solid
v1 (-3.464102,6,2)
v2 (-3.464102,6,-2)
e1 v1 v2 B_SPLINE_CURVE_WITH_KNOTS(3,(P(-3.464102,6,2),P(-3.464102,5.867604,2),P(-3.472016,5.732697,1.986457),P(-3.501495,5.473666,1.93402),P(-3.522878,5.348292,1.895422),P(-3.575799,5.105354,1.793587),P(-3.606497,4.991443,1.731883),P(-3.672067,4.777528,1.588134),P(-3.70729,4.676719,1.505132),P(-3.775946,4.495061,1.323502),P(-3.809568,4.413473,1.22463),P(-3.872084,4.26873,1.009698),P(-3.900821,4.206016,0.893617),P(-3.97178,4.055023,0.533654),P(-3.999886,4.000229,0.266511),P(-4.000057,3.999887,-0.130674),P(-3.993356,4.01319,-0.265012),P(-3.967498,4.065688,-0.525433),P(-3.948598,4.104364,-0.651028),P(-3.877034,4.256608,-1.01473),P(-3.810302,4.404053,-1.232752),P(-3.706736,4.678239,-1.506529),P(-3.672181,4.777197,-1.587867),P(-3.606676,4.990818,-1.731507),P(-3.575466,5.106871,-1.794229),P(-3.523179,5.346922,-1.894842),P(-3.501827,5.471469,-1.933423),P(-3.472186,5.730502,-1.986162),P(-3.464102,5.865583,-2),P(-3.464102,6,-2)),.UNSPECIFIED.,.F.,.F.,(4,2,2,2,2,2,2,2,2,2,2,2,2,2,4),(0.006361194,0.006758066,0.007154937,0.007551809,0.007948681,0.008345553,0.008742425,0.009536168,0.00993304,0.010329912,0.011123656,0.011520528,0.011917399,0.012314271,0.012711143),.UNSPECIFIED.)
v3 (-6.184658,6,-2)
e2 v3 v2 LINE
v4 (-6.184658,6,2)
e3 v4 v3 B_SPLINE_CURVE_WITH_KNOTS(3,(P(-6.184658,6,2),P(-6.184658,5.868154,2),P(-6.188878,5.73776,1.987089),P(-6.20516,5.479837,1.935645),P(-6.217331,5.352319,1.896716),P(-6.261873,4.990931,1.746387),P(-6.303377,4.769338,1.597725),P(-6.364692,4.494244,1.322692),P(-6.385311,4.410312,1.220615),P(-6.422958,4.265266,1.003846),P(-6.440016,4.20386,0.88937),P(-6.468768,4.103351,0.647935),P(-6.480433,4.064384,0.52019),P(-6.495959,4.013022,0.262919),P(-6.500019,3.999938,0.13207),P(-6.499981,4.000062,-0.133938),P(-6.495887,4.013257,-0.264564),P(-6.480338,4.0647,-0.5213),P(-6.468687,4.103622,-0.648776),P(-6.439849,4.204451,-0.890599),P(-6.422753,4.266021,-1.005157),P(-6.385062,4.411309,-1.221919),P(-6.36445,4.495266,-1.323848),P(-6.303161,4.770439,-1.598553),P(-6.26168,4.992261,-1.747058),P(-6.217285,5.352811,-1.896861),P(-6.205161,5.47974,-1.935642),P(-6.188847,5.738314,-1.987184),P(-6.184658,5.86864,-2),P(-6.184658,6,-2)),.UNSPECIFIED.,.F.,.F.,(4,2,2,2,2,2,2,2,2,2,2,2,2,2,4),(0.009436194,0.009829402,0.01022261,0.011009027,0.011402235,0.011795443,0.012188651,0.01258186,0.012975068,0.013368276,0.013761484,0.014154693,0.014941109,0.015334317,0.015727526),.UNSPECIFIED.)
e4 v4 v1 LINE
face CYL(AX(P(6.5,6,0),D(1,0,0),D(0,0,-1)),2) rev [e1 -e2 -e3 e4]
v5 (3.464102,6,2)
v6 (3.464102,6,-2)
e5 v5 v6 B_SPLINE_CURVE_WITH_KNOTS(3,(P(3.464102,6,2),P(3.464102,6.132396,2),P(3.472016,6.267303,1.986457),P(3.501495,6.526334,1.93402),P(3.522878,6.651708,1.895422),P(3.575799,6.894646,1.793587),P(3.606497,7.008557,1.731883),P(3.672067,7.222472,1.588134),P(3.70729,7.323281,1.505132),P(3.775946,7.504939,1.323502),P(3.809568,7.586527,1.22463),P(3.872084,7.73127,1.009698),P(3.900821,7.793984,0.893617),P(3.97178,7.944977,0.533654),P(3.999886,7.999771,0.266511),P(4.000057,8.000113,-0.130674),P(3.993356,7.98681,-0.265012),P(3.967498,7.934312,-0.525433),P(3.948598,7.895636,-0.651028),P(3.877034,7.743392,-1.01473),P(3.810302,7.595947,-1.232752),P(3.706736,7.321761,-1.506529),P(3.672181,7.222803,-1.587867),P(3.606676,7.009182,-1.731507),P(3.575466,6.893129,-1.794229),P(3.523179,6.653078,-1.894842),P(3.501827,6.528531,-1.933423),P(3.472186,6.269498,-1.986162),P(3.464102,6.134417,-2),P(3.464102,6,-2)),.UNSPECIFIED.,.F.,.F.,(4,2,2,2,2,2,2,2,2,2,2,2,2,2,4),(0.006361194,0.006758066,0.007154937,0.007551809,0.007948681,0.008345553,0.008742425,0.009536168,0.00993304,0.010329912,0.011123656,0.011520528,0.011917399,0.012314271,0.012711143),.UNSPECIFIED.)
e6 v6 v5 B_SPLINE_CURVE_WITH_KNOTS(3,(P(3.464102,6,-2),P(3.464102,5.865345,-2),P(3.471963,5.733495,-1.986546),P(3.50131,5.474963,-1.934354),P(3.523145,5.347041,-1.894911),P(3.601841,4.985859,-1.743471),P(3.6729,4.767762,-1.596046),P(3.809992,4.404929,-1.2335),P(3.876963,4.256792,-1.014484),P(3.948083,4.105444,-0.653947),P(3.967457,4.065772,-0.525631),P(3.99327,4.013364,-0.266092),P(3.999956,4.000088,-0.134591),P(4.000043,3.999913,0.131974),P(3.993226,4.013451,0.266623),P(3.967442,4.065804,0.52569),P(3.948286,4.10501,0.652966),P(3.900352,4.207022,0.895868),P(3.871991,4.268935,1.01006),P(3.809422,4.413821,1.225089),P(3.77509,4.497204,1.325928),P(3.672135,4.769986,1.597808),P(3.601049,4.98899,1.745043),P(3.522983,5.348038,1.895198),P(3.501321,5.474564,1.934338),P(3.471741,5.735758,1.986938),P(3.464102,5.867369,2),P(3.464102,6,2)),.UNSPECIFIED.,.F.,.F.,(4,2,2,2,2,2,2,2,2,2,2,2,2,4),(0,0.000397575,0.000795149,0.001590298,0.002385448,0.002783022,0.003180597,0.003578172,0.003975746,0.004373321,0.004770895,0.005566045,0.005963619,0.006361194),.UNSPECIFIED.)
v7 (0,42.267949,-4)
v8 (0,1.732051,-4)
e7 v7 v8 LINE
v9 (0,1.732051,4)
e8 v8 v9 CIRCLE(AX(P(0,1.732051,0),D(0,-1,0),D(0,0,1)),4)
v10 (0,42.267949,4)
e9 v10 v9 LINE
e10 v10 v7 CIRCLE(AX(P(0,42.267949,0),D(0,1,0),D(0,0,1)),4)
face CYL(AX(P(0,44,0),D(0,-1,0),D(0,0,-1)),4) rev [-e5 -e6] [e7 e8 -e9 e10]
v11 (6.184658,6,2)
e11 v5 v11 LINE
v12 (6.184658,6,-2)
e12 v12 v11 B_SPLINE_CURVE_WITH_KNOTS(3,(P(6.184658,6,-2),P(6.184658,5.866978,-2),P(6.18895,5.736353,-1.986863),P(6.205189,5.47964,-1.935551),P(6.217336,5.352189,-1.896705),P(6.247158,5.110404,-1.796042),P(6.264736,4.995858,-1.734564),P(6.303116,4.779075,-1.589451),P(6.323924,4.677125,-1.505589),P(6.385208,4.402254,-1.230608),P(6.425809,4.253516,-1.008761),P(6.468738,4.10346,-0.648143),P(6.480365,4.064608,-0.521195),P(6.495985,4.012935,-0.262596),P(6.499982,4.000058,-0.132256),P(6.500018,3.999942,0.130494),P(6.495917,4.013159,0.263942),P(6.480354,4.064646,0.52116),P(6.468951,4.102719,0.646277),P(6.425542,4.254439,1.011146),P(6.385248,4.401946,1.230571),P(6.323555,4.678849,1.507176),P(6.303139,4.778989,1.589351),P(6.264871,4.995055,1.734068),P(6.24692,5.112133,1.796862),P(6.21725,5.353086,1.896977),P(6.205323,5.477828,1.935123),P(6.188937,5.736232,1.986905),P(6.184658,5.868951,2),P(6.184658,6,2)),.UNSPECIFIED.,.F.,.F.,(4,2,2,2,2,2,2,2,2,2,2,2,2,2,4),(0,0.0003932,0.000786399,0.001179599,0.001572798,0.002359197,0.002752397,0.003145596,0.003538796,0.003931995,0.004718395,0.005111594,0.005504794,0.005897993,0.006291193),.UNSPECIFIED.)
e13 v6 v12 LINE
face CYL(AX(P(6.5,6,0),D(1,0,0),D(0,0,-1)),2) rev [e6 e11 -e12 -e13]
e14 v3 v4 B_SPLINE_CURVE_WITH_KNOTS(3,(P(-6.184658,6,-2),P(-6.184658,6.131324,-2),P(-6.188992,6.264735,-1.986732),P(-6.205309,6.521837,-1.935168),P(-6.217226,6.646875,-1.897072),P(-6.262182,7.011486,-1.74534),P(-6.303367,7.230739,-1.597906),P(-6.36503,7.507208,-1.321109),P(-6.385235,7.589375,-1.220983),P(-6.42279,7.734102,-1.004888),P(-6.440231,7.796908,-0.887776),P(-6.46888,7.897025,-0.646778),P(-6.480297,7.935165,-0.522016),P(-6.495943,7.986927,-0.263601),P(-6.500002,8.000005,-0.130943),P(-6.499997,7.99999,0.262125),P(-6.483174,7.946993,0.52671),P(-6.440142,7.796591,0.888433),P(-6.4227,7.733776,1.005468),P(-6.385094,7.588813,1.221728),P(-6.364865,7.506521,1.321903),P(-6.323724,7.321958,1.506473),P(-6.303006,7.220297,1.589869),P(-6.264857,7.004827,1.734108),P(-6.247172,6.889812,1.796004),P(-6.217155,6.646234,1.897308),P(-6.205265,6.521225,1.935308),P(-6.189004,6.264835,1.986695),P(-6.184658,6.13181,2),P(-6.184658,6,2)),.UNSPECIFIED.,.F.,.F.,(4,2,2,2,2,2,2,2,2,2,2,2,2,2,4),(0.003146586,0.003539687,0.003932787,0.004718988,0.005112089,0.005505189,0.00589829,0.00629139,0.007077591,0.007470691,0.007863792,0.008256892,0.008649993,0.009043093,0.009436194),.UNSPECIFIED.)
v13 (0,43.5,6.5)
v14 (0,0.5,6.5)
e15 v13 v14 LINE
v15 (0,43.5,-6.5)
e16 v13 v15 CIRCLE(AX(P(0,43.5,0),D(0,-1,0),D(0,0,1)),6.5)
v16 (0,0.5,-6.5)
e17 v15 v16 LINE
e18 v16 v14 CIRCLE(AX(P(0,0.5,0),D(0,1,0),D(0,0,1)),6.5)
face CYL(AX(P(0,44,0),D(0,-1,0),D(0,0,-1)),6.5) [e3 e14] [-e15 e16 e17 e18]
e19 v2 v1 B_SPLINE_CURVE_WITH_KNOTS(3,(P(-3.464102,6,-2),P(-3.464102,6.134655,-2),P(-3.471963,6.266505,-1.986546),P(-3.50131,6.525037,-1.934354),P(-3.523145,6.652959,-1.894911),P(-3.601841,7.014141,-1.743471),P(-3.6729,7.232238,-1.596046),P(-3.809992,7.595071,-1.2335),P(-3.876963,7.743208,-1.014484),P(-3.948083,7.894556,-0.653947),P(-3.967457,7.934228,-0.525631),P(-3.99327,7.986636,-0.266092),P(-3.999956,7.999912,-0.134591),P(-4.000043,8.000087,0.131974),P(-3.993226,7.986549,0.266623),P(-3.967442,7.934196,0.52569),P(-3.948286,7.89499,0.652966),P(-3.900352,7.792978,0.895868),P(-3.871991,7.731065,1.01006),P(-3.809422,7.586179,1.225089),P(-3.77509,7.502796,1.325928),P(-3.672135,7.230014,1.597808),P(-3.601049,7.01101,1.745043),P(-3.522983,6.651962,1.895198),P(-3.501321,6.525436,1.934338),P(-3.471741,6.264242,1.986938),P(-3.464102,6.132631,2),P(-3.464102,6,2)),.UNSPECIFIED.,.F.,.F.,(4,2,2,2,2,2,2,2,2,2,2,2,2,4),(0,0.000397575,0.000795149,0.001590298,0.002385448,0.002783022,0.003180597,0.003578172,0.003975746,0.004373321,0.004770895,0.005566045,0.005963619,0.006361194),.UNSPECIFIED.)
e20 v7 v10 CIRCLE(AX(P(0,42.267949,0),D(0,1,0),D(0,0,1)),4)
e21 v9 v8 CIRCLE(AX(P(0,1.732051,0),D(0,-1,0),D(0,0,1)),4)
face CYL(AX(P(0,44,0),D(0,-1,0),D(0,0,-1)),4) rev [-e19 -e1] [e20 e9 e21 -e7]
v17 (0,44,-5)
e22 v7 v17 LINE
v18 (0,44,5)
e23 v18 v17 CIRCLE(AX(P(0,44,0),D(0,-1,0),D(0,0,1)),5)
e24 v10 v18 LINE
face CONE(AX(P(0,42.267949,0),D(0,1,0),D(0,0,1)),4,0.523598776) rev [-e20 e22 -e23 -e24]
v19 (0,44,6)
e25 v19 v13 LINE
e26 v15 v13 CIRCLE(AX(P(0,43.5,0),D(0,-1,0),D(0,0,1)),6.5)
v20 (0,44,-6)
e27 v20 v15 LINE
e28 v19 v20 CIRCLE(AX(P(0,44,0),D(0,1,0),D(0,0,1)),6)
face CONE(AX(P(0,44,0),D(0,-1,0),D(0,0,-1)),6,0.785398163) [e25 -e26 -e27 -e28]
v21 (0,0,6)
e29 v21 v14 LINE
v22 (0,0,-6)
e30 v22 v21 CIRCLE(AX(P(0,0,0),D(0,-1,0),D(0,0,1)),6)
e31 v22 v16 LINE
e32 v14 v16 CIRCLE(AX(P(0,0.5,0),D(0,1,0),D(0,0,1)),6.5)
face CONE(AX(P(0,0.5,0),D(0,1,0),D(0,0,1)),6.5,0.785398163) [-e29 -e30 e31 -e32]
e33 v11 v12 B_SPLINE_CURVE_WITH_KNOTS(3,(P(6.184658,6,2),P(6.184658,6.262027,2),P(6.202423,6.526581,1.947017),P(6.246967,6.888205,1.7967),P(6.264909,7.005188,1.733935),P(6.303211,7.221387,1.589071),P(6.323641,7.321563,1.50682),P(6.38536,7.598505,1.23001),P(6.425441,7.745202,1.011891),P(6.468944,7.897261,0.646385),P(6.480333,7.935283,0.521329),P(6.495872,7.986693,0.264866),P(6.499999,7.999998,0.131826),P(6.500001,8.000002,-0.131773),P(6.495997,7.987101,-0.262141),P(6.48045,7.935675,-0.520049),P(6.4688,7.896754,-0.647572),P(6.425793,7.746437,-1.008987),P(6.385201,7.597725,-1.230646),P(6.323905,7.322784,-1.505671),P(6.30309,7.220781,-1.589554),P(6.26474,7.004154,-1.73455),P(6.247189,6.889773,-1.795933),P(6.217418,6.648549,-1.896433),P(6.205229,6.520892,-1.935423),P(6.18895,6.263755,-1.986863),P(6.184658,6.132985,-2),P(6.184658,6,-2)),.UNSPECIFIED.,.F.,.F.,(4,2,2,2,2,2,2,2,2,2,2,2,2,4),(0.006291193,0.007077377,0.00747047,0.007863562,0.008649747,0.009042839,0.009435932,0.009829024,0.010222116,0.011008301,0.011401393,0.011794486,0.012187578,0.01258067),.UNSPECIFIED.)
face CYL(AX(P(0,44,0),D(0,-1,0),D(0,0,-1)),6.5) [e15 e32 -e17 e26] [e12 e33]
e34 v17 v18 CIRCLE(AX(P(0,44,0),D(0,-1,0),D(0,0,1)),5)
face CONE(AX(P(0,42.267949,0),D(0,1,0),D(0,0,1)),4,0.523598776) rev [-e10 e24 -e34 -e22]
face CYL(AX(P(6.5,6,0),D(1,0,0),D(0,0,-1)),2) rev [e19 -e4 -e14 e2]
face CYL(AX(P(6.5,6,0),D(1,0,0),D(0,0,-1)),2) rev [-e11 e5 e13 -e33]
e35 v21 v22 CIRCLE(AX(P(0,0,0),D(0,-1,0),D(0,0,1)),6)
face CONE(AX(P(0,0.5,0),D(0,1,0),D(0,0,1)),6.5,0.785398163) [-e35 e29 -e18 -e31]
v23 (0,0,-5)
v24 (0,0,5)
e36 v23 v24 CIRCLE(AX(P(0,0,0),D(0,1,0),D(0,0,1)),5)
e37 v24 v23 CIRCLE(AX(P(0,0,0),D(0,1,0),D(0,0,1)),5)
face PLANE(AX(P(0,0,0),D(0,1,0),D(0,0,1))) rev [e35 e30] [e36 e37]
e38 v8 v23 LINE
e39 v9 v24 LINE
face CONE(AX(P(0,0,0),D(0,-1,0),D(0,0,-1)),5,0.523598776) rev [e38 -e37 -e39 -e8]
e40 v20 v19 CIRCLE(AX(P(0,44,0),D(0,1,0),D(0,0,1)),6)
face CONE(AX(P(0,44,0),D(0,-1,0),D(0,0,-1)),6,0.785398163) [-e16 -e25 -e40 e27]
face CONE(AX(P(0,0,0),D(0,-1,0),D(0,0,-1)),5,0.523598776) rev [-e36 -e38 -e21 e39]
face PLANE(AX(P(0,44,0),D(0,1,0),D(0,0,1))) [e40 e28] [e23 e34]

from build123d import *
from OCP.BRepFilletAPI import BRepFilletAPI_MakeChamfer

# Parameters (mm, degrees)
SKETCH_1_R            = 6.5
SKETCH_1_R_2          = 4
EXTRUDE_1_DEPTH       = 44
HOLE_WIZARD_4_0_4_1_D = 4
CHAMFER_1_SIZE        = 0.5
CHAMFER_2_SIZE        = 1
CHAMFER_2_SIZE2       = 1.732050808


with BuildPart() as part:
    # 草图1 → 凸台-拉伸1 (new body)
    with BuildSketch(Plane(origin=(0, 0, 0), x_dir=(1, 0, 0), z_dir=(0, 1, 0))):
        with Locations(Location((0, 0, 0), (0, 0, 270))):
            Circle(SKETCH_1_R)
        with Locations(Location((0, 0, 0), (0, 0, 270))):
            Circle(SKETCH_1_R_2, mode=Mode.SUBTRACT)
    extrude(amount=EXTRUDE_1_DEPTH)

    # Ø4.0 (4) 直径孔1 (through all)
    with Locations(Plane(origin=(6.5, 6, 0), x_dir=(0, 0, 1), z_dir=(1, 0, 0))):
        with Locations((0, 0)):
            Hole(HOLE_WIZARD_4_0_4_1_D / 2)

    # 倒角1
    chamfer_1_edges = [part.edges().sort_by_distance(p)[0] for p in [
        (0, 0, -6.5),
        (0, 44, -6.5),
    ]]
    chamfer(chamfer_1_edges, length=CHAMFER_1_SIZE)

    # 倒角2: one chamfer whose edges measure the first distance from different faces: ONE call of the kernel's chamfer builder (chamfer() names one face for all edges)
    chamfer_2_edges_1 = [part.edges().sort_by_distance(p)[0] for p in [
        (0, 0, -4),
    ]]
    chamfer_2_side_1 = [part.faces().sort_by_distance(p)[0] for p in [
        (0, 0, -5.830294373),
    ]]
    chamfer_2_edges_2 = [part.edges().sort_by_distance(p)[0] for p in [
        (0, 44, -4),
    ]]
    chamfer_2_side_2 = [part.faces().sort_by_distance(p)[0] for p in [
        (0, 44, -5.830294373),
    ]]
    chamfer_2 = BRepFilletAPI_MakeChamfer(part.part.solid().wrapped)
    for e in chamfer_2_edges_1:
        chamfer_2.Add(CHAMFER_2_SIZE, CHAMFER_2_SIZE2, e.wrapped, chamfer_2_side_1[0].wrapped)  # the first distance lies on this face
    for e in chamfer_2_edges_2:
        chamfer_2.Add(CHAMFER_2_SIZE, CHAMFER_2_SIZE2, e.wrapped, chamfer_2_side_2[0].wrapped)  # the first distance lies on this face
    add(Compound.cast(chamfer_2.Shape()), mode=Mode.REPLACE)


solid = part.part
